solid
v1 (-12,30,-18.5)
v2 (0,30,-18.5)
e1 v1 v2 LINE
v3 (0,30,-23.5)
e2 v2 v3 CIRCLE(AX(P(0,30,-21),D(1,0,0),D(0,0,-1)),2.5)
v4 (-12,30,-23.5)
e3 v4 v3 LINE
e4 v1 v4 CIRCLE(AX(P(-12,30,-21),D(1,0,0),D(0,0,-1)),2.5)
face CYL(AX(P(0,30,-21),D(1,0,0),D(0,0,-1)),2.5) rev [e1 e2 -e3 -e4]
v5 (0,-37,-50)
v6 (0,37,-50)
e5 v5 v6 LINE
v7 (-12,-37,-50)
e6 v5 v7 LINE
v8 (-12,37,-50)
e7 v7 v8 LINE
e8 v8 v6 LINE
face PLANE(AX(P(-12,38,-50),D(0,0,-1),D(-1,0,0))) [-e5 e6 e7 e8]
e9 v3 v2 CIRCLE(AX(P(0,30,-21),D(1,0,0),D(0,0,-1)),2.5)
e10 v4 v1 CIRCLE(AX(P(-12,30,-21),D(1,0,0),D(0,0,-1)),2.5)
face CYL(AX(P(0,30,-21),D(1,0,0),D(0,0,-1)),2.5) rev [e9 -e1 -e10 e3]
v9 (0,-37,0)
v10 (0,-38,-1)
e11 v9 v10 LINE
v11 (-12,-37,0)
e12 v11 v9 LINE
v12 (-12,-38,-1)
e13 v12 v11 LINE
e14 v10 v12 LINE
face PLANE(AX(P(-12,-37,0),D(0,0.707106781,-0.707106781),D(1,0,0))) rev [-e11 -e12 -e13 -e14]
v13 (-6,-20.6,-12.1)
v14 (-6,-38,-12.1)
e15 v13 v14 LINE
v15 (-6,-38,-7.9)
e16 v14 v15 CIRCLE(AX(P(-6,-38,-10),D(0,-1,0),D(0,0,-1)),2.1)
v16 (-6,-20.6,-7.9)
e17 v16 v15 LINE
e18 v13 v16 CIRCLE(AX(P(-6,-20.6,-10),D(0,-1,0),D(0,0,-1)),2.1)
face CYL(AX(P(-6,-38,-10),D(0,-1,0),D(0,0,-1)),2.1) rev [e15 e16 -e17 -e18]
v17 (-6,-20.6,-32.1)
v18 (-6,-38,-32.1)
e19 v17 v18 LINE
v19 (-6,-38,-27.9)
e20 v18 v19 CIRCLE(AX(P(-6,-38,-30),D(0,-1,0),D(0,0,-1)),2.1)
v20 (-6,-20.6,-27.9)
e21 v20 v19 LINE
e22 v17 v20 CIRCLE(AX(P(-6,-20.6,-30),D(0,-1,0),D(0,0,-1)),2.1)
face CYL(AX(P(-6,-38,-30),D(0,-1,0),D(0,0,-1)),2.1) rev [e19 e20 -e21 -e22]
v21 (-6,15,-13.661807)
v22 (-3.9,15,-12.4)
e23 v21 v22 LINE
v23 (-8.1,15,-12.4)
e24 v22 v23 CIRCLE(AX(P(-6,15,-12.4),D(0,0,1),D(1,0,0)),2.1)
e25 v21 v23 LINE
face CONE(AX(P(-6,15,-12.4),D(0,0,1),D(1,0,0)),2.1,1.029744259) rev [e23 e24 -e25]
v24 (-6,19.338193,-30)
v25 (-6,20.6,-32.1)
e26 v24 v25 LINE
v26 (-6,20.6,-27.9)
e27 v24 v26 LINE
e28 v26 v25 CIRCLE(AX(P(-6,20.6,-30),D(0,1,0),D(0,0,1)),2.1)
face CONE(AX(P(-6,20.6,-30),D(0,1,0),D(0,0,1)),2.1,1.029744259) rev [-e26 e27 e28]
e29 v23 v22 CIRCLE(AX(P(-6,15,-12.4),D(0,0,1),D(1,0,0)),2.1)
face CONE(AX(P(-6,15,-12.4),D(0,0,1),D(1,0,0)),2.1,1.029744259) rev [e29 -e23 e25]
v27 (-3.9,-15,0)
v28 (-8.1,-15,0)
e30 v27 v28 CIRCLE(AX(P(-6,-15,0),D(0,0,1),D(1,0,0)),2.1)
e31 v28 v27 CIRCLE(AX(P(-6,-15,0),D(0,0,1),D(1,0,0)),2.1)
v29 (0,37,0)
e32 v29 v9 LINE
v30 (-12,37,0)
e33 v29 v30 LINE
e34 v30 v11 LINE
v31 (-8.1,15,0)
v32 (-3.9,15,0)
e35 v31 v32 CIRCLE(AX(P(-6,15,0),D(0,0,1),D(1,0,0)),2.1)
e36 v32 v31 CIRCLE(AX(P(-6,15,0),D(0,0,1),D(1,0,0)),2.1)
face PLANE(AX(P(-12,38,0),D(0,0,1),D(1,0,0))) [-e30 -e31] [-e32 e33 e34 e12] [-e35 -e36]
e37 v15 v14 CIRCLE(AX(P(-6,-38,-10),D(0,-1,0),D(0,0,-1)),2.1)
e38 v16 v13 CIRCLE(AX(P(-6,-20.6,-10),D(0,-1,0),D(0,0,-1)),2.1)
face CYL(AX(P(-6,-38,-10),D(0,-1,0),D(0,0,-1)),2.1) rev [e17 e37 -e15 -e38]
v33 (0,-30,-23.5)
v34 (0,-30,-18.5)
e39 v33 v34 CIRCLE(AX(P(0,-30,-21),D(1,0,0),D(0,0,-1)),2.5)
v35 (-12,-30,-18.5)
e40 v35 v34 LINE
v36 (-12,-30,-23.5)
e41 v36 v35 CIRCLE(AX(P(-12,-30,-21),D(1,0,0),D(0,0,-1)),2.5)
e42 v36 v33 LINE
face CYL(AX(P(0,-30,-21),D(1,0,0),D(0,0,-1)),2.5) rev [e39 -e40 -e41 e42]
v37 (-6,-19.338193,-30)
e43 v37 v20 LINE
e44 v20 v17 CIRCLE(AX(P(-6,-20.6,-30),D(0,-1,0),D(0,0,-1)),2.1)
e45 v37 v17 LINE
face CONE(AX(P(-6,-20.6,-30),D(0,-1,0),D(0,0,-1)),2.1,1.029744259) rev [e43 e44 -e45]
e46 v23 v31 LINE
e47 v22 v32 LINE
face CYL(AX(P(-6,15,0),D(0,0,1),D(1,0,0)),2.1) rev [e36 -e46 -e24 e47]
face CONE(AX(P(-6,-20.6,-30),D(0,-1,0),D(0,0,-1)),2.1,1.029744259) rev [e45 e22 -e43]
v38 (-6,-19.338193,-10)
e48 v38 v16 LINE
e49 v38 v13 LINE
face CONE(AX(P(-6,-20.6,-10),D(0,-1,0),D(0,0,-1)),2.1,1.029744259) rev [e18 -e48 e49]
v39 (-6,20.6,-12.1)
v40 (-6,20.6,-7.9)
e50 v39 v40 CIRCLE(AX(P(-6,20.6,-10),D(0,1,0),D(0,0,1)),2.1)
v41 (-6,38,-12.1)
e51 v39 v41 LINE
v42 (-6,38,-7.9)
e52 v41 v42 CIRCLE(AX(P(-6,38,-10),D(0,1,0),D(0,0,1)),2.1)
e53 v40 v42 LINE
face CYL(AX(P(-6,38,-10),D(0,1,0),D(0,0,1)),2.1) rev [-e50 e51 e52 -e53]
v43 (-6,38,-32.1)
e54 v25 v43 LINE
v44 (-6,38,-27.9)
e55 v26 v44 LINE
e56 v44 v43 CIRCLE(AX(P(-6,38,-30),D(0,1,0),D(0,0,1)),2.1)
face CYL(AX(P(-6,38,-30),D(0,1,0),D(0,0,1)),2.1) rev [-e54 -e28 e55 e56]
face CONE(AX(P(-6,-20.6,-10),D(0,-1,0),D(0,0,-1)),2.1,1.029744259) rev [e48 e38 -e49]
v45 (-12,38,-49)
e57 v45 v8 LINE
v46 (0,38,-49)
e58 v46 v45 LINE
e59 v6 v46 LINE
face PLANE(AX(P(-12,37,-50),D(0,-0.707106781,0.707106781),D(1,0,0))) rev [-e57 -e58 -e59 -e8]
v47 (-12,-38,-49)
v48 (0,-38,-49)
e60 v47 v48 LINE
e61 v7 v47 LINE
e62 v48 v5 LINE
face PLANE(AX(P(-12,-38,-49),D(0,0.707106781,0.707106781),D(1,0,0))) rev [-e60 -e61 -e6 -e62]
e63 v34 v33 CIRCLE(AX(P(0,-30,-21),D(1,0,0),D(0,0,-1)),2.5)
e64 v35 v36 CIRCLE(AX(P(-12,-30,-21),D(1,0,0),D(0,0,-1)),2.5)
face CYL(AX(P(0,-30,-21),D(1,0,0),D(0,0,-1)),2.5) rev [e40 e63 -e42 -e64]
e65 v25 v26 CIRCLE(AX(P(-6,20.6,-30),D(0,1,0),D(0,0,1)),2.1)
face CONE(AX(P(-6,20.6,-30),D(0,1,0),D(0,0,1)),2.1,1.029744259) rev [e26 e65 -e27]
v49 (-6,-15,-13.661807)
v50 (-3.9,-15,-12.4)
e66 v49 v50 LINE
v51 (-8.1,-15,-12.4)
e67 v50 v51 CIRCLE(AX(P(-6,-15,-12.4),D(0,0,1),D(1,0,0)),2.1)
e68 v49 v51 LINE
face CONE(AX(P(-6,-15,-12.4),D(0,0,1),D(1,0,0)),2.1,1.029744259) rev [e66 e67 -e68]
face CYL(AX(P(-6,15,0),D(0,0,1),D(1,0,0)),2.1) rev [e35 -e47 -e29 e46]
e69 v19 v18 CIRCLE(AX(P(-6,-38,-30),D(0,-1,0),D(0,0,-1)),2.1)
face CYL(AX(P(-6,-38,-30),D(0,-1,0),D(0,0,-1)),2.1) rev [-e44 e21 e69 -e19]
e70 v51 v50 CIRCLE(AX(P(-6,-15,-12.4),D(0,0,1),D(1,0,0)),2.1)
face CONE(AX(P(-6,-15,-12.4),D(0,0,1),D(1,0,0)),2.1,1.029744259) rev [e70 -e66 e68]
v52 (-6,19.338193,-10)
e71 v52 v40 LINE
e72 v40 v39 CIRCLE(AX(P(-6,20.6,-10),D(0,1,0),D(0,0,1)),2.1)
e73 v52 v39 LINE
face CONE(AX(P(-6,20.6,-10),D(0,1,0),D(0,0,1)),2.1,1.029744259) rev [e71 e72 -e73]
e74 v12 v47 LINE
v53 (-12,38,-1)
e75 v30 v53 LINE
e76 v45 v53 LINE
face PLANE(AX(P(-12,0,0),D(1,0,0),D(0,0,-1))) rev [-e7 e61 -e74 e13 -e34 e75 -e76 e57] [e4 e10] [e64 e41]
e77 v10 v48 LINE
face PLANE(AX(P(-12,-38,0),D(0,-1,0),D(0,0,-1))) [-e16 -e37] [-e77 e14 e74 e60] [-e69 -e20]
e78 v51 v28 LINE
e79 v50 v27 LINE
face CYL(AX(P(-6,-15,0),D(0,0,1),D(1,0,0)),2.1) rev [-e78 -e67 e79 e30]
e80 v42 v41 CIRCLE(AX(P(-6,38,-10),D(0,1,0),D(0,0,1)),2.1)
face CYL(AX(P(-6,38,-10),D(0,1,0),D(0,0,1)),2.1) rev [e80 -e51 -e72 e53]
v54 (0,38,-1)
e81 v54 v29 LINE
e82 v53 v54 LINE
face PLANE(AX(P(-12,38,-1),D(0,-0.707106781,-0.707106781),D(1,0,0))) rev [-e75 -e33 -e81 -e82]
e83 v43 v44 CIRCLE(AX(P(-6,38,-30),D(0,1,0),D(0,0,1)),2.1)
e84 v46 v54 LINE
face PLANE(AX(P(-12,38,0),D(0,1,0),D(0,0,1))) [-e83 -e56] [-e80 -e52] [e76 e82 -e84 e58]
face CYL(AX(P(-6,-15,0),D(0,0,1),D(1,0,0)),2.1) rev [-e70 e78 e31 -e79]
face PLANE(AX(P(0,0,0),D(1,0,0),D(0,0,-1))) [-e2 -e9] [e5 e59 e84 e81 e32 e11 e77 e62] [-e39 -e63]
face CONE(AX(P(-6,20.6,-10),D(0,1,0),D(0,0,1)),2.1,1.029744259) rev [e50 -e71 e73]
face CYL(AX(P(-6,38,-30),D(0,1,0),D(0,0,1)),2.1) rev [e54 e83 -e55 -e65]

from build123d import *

# Parameters (mm, degrees)
SKETCH6_W                  = 50
SKETCH6_H                  = 76
BOSS_EXTRUDE6_DEPTH        = 12
M6_TAPPED_HOLE2_D          = 5
M6_TAPPED_HOLE2_DEPTH      = 15
M6_TAPPED_HOLE2_TIP        = 1.502151548
M5_TAPPED_HOLE3_AT_2_COUNT = 2
M5_TAPPED_HOLE3_AT_2_PITCH = 20
M5_TAPPED_HOLE2_D          = 4.2
M5_TAPPED_HOLE2_DEPTH      = 12.4
M5_TAPPED_HOLE2_TIP        = 1.2618073
CHAMFER1_SIZE              = 1


with BuildPart() as part:
    # Sketch6 → Boss-Extrude6 (new body)
    with BuildSketch(Plane(origin=(0, 0, 0), x_dir=(0, 0, -1), z_dir=(1, 0, 0))):
        with Locations((25, 0)):
            Rectangle(SKETCH6_W, SKETCH6_H)
    extrude(amount=-BOSS_EXTRUDE6_DEPTH)

    # M6 Tapped Hole2
    with Locations(Plane(origin=(0, 0, 0), x_dir=(0, 0, -1), z_dir=(1, 0, 0))):
        with Locations((21, -30), (21, 30)):
            Hole(M6_TAPPED_HOLE2_D / 2, depth=M6_TAPPED_HOLE2_DEPTH)
            with Locations((0, 0, -(M6_TAPPED_HOLE2_DEPTH + M6_TAPPED_HOLE2_TIP / 2))):  # 118° drill point
                Cone(0, M6_TAPPED_HOLE2_D / 2, M6_TAPPED_HOLE2_TIP, mode=Mode.SUBTRACT)

    # Sketch19 → M5 Tapped Hole3 (revolve, cut)
    with BuildSketch(Plane(origin=(-6, -38, -10), x_dir=(0, 0, -1), z_dir=(1, 0, 0))):
        Polygon((0, 0), (0, 18.6618073), (2.1, 17.4), (2.1, 0), align=None)
    m5_tapped_hole3 = revolve(axis=Axis((-6, -44.35, -10), (0, 1, 0)), mode=Mode.SUBTRACT)

    # M5 Tapped Hole3 at 2: M5 Tapped Hole3 ×2
    with Locations(*[(0, 0, -i * M5_TAPPED_HOLE3_AT_2_PITCH) for i in range(1, M5_TAPPED_HOLE3_AT_2_COUNT)]):
        add(m5_tapped_hole3, mode=Mode.SUBTRACT)

    # Mirror1: M5 Tapped Hole3 across plane
    add(m5_tapped_hole3.mirror(Plane.ZX), mode=Mode.SUBTRACT)

    # Mirror1 copy 1 sketch → Mirror1 copy 1 (revolve, cut)
    with BuildSketch(Plane(origin=(-6, 38, -30), x_dir=(0, 0, -1), z_dir=(1, 0, 0))):
        Polygon((0, 0), (0, -18.6618073), (2.1, -17.4), (2.1, 0), align=None)
    revolve(axis=Axis((-6, 44.35, -30), (0, 1, 0)), mode=Mode.SUBTRACT)

    # M5 Tapped Hole2
    with Locations(Plane.XY):
        with Locations((-6, 15), (-6, -15)):
            Hole(M5_TAPPED_HOLE2_D / 2, depth=M5_TAPPED_HOLE2_DEPTH)
            with Locations((0, 0, -(M5_TAPPED_HOLE2_DEPTH + M5_TAPPED_HOLE2_TIP / 2))):  # 118° drill point
                Cone(0, M5_TAPPED_HOLE2_D / 2, M5_TAPPED_HOLE2_TIP, mode=Mode.SUBTRACT)

    # Chamfer1
    chamfer1_edges = [part.edges().sort_by_distance(p)[0] for p in [
        (-6, 38, 0),
        (-6, 38, -50),
        (-6, -38, -50),
        (-6, -38, 0),
    ]]
    chamfer(chamfer1_edges, length=CHAMFER1_SIZE)


solid = part.part
